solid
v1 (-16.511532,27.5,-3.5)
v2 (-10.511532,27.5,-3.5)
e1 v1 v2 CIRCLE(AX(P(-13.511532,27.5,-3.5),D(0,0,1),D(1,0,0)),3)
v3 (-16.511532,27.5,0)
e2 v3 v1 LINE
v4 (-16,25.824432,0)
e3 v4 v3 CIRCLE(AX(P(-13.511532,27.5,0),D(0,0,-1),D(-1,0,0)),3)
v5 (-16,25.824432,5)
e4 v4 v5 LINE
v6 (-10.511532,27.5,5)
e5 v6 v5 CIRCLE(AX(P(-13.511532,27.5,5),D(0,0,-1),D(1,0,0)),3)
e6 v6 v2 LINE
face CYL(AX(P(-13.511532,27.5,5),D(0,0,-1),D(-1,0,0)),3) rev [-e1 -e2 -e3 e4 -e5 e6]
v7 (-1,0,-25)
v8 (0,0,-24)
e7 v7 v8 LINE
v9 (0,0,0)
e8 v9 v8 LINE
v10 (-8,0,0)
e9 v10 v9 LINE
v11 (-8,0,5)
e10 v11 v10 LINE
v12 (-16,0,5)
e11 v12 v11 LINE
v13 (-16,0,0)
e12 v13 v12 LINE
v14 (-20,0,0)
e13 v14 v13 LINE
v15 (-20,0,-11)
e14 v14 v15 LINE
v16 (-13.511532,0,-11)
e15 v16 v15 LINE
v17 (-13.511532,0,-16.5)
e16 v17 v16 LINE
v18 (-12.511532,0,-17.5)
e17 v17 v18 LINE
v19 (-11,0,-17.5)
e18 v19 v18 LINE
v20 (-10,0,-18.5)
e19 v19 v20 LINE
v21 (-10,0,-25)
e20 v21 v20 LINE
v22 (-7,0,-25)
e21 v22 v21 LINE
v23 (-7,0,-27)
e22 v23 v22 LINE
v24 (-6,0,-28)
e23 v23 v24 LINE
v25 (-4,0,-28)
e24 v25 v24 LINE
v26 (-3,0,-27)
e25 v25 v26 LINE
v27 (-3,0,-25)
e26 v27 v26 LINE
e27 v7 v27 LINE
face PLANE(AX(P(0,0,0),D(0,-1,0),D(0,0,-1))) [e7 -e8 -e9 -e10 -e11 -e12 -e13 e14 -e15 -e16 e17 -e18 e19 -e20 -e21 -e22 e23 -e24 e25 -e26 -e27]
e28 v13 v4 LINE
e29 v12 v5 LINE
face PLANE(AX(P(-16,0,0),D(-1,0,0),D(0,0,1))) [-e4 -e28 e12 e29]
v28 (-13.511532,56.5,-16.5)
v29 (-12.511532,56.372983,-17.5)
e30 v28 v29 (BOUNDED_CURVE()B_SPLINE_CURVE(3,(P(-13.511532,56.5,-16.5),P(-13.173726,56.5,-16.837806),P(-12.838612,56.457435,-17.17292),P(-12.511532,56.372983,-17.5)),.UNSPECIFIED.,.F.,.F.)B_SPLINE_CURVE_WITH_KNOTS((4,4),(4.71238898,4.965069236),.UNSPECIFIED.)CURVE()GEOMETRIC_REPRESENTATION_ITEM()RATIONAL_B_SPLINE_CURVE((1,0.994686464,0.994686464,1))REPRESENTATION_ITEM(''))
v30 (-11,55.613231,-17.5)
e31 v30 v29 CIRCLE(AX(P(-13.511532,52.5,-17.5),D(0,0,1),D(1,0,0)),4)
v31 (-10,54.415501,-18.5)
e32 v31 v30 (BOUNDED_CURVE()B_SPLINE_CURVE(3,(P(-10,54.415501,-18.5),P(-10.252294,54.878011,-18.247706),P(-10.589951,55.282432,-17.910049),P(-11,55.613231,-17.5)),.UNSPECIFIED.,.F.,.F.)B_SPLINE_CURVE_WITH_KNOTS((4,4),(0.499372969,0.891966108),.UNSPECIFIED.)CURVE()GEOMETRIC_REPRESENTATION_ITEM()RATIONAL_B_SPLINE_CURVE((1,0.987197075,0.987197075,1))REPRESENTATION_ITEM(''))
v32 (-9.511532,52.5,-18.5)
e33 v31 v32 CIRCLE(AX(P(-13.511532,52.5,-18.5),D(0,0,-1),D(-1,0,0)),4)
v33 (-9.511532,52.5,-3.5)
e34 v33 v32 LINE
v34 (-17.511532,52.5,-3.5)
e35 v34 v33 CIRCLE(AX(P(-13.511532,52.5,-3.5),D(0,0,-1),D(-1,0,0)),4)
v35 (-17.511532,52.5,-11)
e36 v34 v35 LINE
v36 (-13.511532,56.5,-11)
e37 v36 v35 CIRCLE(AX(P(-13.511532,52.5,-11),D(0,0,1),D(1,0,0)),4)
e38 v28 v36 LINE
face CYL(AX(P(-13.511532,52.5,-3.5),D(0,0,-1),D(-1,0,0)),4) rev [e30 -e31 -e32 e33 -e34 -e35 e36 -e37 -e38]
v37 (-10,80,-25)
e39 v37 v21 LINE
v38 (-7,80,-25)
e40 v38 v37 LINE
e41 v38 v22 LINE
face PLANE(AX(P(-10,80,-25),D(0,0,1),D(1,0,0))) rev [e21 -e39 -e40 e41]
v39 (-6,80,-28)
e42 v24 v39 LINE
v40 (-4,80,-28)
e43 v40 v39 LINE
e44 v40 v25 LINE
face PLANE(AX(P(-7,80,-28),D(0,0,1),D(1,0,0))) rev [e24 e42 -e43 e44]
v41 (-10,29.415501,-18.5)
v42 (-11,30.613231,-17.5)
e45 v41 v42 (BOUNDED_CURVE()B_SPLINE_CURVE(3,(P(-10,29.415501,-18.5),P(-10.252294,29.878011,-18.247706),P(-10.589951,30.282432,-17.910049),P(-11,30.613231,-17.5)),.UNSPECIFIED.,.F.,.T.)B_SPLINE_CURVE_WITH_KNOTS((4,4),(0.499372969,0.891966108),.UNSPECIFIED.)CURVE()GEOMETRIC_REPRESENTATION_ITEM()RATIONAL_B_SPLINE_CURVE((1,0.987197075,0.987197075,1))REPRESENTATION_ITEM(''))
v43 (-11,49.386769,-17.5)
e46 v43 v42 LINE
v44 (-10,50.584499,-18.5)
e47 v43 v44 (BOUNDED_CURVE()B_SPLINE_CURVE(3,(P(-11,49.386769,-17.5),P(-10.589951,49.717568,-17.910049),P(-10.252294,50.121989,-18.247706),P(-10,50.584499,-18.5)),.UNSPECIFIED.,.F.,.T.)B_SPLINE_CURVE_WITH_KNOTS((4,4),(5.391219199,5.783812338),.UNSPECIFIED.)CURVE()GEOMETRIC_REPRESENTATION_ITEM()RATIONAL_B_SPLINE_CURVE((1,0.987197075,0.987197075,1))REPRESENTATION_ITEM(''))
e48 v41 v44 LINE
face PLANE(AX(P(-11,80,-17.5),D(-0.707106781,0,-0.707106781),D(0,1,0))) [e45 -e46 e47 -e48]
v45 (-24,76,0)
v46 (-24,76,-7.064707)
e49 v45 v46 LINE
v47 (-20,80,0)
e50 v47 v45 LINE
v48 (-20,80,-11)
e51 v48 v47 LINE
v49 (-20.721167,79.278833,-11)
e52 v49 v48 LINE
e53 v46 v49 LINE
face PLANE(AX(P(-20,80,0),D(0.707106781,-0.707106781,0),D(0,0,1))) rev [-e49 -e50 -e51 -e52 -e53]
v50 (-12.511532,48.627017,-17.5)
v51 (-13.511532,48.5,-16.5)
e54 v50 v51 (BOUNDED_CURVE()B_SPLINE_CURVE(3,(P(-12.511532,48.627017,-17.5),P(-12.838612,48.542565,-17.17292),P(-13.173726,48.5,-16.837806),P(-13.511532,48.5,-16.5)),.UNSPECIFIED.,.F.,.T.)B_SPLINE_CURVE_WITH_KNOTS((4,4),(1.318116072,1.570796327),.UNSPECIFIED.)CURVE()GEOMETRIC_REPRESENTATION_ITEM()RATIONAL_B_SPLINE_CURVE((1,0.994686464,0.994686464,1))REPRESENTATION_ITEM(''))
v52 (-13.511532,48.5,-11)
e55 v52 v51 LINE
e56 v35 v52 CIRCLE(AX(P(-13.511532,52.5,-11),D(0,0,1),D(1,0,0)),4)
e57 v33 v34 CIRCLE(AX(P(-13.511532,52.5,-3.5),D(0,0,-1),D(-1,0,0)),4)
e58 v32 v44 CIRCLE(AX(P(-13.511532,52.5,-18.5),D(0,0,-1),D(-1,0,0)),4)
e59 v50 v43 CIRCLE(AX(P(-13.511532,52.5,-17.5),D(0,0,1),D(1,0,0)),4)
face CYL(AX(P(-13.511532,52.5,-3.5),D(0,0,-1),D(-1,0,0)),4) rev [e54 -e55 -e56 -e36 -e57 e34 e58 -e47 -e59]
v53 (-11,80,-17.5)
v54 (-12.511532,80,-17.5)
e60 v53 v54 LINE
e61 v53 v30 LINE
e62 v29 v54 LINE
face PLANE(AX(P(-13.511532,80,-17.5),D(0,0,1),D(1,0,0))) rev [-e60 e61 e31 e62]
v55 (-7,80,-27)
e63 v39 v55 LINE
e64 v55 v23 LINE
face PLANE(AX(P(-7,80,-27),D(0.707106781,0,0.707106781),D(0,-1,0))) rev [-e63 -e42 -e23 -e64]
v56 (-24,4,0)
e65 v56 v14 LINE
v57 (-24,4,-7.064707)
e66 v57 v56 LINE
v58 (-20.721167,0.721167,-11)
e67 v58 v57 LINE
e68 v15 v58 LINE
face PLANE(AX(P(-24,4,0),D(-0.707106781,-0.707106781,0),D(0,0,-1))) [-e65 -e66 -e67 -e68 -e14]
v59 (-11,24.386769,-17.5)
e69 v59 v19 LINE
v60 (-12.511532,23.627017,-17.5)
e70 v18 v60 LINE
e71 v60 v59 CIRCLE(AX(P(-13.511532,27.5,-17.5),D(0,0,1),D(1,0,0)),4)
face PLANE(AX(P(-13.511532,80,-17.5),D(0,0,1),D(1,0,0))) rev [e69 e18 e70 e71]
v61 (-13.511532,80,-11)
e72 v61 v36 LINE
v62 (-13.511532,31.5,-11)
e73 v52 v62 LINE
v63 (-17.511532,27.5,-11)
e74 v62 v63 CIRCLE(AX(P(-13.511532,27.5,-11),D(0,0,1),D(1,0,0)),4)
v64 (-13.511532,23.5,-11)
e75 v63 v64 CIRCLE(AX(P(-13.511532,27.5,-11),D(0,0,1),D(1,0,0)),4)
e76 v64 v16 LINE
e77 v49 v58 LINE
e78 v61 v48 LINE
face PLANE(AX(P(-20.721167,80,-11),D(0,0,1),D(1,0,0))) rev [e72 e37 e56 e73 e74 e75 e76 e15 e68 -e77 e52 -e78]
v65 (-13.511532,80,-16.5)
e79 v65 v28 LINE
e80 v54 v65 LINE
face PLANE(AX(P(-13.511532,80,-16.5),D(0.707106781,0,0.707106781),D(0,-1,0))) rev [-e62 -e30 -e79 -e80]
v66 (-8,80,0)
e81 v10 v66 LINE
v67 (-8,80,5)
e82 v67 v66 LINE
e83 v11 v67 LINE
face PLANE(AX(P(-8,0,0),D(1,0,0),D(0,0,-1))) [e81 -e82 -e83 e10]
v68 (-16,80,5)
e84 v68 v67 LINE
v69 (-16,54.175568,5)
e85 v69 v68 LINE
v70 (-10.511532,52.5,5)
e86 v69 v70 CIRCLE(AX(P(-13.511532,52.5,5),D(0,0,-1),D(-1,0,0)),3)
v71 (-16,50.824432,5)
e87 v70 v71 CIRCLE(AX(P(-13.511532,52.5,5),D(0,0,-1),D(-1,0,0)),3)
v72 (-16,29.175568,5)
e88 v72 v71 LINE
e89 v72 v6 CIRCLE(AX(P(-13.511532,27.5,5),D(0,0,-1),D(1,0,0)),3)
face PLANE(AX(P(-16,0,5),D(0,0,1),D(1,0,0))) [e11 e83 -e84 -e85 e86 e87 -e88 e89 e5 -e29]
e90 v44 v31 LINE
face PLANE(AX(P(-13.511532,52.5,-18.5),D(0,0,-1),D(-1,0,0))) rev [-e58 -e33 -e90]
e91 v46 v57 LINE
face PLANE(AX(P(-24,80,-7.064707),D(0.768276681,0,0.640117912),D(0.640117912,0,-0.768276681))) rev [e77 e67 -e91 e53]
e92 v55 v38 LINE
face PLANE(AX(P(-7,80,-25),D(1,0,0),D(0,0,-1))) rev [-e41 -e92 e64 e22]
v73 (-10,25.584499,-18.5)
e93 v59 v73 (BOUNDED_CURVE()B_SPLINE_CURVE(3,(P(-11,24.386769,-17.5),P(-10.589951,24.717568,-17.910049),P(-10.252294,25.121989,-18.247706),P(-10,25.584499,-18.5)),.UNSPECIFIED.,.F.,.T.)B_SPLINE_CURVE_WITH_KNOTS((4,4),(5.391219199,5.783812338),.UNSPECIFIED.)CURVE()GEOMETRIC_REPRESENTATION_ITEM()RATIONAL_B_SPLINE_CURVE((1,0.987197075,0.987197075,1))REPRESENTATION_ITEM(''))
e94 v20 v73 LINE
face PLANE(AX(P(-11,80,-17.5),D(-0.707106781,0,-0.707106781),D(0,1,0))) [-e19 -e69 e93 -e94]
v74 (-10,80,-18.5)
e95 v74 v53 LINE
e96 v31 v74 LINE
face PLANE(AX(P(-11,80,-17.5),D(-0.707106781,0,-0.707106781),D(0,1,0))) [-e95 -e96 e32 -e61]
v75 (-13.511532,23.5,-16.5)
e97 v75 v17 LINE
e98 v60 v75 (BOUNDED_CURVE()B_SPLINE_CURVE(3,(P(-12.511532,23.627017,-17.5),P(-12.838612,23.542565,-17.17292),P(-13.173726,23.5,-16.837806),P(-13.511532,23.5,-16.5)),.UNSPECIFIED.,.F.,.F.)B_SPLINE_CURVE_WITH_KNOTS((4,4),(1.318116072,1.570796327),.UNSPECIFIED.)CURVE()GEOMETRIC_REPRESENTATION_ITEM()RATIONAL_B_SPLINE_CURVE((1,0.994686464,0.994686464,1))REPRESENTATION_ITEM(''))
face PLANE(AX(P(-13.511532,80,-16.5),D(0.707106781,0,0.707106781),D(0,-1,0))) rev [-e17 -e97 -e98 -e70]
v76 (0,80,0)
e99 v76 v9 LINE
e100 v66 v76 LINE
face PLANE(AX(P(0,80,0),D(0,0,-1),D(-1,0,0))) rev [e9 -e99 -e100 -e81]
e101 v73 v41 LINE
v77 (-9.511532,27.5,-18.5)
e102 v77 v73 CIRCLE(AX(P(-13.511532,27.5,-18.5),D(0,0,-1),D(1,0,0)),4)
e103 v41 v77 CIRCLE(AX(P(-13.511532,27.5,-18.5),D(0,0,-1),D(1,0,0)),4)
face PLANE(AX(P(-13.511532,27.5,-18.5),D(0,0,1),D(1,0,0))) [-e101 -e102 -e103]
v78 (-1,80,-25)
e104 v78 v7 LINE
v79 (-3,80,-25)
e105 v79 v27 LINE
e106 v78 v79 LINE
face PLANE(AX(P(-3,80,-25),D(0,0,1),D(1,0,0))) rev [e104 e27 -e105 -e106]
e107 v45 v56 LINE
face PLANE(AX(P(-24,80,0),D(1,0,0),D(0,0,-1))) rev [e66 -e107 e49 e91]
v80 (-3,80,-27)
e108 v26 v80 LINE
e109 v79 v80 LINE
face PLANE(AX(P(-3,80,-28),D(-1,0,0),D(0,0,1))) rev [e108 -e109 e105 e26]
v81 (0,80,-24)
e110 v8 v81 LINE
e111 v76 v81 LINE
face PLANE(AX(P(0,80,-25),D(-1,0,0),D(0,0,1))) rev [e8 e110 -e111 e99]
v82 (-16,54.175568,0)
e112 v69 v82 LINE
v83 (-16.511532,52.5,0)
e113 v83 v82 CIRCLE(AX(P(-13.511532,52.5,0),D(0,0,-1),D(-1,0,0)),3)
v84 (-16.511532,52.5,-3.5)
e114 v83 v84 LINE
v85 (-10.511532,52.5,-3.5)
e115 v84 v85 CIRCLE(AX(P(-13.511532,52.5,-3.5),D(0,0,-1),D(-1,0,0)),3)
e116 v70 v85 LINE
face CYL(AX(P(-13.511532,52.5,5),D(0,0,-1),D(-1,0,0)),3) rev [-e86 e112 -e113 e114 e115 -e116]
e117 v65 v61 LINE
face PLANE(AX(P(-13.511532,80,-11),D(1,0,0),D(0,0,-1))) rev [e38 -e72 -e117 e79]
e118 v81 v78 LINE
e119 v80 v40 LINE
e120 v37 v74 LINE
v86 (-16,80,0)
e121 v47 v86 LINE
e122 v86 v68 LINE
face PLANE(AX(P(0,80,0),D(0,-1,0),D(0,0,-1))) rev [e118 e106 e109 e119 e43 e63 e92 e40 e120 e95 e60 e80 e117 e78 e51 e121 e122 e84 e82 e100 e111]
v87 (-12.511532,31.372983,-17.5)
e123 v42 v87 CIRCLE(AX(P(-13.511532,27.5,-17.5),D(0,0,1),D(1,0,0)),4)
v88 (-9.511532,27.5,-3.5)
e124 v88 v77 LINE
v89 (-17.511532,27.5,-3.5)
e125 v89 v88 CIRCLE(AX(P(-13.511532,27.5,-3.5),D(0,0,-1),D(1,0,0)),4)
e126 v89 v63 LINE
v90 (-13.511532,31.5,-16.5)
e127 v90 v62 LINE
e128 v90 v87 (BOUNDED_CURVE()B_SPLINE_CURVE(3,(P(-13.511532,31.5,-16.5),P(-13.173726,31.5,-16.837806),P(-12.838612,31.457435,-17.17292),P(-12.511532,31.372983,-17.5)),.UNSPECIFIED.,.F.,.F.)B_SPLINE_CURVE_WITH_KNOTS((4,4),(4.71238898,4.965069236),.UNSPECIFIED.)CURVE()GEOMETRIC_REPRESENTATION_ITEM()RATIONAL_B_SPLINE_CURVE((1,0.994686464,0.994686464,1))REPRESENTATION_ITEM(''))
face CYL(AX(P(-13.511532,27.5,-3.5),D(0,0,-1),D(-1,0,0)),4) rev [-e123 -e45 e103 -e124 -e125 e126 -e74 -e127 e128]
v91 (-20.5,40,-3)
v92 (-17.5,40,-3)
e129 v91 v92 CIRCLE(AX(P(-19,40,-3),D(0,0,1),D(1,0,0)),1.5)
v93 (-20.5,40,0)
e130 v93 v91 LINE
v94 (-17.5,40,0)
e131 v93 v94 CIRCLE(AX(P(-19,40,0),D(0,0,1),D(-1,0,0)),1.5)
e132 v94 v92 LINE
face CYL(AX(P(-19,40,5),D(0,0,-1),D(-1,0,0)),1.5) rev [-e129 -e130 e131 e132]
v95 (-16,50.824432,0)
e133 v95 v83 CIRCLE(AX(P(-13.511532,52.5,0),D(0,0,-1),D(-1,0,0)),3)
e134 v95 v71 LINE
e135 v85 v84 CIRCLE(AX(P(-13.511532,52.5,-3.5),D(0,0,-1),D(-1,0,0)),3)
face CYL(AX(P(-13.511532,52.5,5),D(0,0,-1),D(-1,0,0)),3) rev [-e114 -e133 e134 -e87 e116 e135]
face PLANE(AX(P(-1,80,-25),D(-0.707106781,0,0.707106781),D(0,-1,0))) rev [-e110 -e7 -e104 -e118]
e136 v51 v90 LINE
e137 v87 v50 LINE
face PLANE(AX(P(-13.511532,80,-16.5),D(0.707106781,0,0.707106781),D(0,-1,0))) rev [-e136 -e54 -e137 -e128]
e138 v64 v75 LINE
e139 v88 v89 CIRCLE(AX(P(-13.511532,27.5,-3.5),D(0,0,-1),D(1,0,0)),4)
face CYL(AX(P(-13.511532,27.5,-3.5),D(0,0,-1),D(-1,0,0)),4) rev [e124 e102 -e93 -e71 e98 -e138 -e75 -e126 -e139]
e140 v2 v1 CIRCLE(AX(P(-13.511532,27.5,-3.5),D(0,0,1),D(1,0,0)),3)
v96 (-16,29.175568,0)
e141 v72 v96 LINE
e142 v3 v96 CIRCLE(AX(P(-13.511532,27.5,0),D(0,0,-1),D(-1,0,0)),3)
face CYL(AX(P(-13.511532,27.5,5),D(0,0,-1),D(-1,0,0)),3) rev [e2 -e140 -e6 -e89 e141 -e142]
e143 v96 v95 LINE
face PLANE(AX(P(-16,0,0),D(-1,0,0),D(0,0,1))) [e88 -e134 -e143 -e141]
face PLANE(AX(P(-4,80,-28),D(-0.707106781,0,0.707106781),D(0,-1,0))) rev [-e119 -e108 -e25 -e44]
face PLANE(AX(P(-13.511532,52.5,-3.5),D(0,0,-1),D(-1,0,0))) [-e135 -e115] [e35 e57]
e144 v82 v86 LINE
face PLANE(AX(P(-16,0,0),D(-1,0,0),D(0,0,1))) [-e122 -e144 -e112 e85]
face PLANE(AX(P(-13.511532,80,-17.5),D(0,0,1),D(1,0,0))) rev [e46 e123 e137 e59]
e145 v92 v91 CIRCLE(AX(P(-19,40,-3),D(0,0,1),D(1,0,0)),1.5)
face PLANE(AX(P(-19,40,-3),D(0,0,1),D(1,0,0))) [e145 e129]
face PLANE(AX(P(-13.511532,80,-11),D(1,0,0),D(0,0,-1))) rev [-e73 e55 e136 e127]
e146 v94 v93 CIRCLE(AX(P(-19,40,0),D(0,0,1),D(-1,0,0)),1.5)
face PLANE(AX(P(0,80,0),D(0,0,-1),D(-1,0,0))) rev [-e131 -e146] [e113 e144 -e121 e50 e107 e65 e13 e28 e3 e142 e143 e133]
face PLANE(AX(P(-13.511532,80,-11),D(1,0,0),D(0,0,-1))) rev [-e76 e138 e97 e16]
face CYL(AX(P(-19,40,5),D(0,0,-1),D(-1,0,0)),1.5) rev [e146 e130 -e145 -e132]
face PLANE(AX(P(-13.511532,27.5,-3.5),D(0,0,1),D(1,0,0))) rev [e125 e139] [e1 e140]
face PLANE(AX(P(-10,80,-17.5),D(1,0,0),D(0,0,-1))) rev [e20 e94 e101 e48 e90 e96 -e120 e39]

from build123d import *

# Parameters (mm, degrees)
BOSS_EXTRUDE1_DEPTH     = 80
CHAMFER1_SIZE           = 1
CHAMFER2_SIZE           = 4
SKETCH2_W               = 8
SKETCH2_H               = 5
BOSS_EXTRUDE2_DEPTH     = 80
SKETCH3_R               = 4
CUT_EXTRUDE1_DEPTH      = 7.5
CUT_EXTRUDE2_DEPTH      = 86.234969349
CUT_EXTRUDE2_DEPTH_BACK = 86.234969349
SKETCH4_R               = 3
CUT_EXTRUDE3_DEPTH      = 89.090862182
CUT_EXTRUDE3_DEPTH_BACK = 3
SKETCH5_R               = 1.5


with BuildPart() as part:
    # Sketch1 → Boss-Extrude1 (new body)
    with BuildSketch(Plane(origin=(0, 0, 0), x_dir=(1, 0, 0), z_dir=(0, 1, 0))):
        Polygon((0, 25), (0, 0), (-24, 0), (-24, 7.06470747), (-20.721166606, 11), (-13.511532016, 11), (-13.511532016, 17.5), (-10, 17.5), (-10, 25), (-7, 25), (-7, 28), (-3, 28), (-3, 25), align=None)
    extrude(amount=BOSS_EXTRUDE1_DEPTH)

    # Chamfer1
    chamfer1_edges = [part.edges().sort_by_distance(p)[0] for p in [
        (-13.511532016, 40, -17.5),
        (-10, 40, -17.5),
        (-7, 40, -28),
        (-3, 40, -28),
        (0, 40, -25),
    ]]
    chamfer(chamfer1_edges, length=CHAMFER1_SIZE)

    # Chamfer2
    chamfer2_edges = [part.edges().sort_by_distance(p)[0] for p in [
        (-24, 80, -3.532353735),
        (-24, 0, -3.532353735),
    ]]
    chamfer(chamfer2_edges, length=CHAMFER2_SIZE)

    # Sketch2 → Boss-Extrude2 (add)
    with BuildSketch(Plane(origin=(0, 80, 0), x_dir=(1, 0, 0), z_dir=(0, 1, 0))):
        with Locations((-12, -2.5)):
            Rectangle(SKETCH2_W, SKETCH2_H)
    extrude(amount=-BOSS_EXTRUDE2_DEPTH)

    # Sketch3 → Cut-Extrude1 (cut, symmetric)
    with BuildSketch(Plane(origin=(0, 0, -11), x_dir=(-1, 0, 0), z_dir=(0, 0, -1))):
        with Locations((13.511532016, 52.5)):
            Circle(SKETCH3_R)
        with Locations(Location((13.511532016, 27.5, 0), (0, 0, 90))):
            Circle(SKETCH3_R)
    extrude(amount=CUT_EXTRUDE1_DEPTH, both=True, mode=Mode.SUBTRACT)

    # Sketch4 → Cut-Extrude2 (cut, two sides: drawn at the far end of the back side and taken through both)
    with BuildSketch(Plane(origin=(0, 0, -11), x_dir=(-1, 0, 0), z_dir=(0, 0, -1)).offset(-CUT_EXTRUDE2_DEPTH_BACK)):
        with Locations((13.511532016, 52.5)):
            Circle(SKETCH4_R)
        with Locations(Location((13.511532016, 27.5, 0), (0, 0, 33.953684666))):
            Circle(SKETCH4_R)
    extrude(amount=CUT_EXTRUDE2_DEPTH + CUT_EXTRUDE2_DEPTH_BACK, mode=Mode.SUBTRACT)

    # Sketch5 → Cut-Extrude3 (cut, two sides: drawn at the far end of the back side and taken through both)
    with BuildSketch(Plane.XY.offset(-CUT_EXTRUDE3_DEPTH_BACK)):
        with Locations(Location((-19, 40, 0), (0, 0, 180))):
            Circle(SKETCH5_R)
    extrude(amount=CUT_EXTRUDE3_DEPTH + CUT_EXTRUDE3_DEPTH_BACK, mode=Mode.SUBTRACT)


solid = part.part
